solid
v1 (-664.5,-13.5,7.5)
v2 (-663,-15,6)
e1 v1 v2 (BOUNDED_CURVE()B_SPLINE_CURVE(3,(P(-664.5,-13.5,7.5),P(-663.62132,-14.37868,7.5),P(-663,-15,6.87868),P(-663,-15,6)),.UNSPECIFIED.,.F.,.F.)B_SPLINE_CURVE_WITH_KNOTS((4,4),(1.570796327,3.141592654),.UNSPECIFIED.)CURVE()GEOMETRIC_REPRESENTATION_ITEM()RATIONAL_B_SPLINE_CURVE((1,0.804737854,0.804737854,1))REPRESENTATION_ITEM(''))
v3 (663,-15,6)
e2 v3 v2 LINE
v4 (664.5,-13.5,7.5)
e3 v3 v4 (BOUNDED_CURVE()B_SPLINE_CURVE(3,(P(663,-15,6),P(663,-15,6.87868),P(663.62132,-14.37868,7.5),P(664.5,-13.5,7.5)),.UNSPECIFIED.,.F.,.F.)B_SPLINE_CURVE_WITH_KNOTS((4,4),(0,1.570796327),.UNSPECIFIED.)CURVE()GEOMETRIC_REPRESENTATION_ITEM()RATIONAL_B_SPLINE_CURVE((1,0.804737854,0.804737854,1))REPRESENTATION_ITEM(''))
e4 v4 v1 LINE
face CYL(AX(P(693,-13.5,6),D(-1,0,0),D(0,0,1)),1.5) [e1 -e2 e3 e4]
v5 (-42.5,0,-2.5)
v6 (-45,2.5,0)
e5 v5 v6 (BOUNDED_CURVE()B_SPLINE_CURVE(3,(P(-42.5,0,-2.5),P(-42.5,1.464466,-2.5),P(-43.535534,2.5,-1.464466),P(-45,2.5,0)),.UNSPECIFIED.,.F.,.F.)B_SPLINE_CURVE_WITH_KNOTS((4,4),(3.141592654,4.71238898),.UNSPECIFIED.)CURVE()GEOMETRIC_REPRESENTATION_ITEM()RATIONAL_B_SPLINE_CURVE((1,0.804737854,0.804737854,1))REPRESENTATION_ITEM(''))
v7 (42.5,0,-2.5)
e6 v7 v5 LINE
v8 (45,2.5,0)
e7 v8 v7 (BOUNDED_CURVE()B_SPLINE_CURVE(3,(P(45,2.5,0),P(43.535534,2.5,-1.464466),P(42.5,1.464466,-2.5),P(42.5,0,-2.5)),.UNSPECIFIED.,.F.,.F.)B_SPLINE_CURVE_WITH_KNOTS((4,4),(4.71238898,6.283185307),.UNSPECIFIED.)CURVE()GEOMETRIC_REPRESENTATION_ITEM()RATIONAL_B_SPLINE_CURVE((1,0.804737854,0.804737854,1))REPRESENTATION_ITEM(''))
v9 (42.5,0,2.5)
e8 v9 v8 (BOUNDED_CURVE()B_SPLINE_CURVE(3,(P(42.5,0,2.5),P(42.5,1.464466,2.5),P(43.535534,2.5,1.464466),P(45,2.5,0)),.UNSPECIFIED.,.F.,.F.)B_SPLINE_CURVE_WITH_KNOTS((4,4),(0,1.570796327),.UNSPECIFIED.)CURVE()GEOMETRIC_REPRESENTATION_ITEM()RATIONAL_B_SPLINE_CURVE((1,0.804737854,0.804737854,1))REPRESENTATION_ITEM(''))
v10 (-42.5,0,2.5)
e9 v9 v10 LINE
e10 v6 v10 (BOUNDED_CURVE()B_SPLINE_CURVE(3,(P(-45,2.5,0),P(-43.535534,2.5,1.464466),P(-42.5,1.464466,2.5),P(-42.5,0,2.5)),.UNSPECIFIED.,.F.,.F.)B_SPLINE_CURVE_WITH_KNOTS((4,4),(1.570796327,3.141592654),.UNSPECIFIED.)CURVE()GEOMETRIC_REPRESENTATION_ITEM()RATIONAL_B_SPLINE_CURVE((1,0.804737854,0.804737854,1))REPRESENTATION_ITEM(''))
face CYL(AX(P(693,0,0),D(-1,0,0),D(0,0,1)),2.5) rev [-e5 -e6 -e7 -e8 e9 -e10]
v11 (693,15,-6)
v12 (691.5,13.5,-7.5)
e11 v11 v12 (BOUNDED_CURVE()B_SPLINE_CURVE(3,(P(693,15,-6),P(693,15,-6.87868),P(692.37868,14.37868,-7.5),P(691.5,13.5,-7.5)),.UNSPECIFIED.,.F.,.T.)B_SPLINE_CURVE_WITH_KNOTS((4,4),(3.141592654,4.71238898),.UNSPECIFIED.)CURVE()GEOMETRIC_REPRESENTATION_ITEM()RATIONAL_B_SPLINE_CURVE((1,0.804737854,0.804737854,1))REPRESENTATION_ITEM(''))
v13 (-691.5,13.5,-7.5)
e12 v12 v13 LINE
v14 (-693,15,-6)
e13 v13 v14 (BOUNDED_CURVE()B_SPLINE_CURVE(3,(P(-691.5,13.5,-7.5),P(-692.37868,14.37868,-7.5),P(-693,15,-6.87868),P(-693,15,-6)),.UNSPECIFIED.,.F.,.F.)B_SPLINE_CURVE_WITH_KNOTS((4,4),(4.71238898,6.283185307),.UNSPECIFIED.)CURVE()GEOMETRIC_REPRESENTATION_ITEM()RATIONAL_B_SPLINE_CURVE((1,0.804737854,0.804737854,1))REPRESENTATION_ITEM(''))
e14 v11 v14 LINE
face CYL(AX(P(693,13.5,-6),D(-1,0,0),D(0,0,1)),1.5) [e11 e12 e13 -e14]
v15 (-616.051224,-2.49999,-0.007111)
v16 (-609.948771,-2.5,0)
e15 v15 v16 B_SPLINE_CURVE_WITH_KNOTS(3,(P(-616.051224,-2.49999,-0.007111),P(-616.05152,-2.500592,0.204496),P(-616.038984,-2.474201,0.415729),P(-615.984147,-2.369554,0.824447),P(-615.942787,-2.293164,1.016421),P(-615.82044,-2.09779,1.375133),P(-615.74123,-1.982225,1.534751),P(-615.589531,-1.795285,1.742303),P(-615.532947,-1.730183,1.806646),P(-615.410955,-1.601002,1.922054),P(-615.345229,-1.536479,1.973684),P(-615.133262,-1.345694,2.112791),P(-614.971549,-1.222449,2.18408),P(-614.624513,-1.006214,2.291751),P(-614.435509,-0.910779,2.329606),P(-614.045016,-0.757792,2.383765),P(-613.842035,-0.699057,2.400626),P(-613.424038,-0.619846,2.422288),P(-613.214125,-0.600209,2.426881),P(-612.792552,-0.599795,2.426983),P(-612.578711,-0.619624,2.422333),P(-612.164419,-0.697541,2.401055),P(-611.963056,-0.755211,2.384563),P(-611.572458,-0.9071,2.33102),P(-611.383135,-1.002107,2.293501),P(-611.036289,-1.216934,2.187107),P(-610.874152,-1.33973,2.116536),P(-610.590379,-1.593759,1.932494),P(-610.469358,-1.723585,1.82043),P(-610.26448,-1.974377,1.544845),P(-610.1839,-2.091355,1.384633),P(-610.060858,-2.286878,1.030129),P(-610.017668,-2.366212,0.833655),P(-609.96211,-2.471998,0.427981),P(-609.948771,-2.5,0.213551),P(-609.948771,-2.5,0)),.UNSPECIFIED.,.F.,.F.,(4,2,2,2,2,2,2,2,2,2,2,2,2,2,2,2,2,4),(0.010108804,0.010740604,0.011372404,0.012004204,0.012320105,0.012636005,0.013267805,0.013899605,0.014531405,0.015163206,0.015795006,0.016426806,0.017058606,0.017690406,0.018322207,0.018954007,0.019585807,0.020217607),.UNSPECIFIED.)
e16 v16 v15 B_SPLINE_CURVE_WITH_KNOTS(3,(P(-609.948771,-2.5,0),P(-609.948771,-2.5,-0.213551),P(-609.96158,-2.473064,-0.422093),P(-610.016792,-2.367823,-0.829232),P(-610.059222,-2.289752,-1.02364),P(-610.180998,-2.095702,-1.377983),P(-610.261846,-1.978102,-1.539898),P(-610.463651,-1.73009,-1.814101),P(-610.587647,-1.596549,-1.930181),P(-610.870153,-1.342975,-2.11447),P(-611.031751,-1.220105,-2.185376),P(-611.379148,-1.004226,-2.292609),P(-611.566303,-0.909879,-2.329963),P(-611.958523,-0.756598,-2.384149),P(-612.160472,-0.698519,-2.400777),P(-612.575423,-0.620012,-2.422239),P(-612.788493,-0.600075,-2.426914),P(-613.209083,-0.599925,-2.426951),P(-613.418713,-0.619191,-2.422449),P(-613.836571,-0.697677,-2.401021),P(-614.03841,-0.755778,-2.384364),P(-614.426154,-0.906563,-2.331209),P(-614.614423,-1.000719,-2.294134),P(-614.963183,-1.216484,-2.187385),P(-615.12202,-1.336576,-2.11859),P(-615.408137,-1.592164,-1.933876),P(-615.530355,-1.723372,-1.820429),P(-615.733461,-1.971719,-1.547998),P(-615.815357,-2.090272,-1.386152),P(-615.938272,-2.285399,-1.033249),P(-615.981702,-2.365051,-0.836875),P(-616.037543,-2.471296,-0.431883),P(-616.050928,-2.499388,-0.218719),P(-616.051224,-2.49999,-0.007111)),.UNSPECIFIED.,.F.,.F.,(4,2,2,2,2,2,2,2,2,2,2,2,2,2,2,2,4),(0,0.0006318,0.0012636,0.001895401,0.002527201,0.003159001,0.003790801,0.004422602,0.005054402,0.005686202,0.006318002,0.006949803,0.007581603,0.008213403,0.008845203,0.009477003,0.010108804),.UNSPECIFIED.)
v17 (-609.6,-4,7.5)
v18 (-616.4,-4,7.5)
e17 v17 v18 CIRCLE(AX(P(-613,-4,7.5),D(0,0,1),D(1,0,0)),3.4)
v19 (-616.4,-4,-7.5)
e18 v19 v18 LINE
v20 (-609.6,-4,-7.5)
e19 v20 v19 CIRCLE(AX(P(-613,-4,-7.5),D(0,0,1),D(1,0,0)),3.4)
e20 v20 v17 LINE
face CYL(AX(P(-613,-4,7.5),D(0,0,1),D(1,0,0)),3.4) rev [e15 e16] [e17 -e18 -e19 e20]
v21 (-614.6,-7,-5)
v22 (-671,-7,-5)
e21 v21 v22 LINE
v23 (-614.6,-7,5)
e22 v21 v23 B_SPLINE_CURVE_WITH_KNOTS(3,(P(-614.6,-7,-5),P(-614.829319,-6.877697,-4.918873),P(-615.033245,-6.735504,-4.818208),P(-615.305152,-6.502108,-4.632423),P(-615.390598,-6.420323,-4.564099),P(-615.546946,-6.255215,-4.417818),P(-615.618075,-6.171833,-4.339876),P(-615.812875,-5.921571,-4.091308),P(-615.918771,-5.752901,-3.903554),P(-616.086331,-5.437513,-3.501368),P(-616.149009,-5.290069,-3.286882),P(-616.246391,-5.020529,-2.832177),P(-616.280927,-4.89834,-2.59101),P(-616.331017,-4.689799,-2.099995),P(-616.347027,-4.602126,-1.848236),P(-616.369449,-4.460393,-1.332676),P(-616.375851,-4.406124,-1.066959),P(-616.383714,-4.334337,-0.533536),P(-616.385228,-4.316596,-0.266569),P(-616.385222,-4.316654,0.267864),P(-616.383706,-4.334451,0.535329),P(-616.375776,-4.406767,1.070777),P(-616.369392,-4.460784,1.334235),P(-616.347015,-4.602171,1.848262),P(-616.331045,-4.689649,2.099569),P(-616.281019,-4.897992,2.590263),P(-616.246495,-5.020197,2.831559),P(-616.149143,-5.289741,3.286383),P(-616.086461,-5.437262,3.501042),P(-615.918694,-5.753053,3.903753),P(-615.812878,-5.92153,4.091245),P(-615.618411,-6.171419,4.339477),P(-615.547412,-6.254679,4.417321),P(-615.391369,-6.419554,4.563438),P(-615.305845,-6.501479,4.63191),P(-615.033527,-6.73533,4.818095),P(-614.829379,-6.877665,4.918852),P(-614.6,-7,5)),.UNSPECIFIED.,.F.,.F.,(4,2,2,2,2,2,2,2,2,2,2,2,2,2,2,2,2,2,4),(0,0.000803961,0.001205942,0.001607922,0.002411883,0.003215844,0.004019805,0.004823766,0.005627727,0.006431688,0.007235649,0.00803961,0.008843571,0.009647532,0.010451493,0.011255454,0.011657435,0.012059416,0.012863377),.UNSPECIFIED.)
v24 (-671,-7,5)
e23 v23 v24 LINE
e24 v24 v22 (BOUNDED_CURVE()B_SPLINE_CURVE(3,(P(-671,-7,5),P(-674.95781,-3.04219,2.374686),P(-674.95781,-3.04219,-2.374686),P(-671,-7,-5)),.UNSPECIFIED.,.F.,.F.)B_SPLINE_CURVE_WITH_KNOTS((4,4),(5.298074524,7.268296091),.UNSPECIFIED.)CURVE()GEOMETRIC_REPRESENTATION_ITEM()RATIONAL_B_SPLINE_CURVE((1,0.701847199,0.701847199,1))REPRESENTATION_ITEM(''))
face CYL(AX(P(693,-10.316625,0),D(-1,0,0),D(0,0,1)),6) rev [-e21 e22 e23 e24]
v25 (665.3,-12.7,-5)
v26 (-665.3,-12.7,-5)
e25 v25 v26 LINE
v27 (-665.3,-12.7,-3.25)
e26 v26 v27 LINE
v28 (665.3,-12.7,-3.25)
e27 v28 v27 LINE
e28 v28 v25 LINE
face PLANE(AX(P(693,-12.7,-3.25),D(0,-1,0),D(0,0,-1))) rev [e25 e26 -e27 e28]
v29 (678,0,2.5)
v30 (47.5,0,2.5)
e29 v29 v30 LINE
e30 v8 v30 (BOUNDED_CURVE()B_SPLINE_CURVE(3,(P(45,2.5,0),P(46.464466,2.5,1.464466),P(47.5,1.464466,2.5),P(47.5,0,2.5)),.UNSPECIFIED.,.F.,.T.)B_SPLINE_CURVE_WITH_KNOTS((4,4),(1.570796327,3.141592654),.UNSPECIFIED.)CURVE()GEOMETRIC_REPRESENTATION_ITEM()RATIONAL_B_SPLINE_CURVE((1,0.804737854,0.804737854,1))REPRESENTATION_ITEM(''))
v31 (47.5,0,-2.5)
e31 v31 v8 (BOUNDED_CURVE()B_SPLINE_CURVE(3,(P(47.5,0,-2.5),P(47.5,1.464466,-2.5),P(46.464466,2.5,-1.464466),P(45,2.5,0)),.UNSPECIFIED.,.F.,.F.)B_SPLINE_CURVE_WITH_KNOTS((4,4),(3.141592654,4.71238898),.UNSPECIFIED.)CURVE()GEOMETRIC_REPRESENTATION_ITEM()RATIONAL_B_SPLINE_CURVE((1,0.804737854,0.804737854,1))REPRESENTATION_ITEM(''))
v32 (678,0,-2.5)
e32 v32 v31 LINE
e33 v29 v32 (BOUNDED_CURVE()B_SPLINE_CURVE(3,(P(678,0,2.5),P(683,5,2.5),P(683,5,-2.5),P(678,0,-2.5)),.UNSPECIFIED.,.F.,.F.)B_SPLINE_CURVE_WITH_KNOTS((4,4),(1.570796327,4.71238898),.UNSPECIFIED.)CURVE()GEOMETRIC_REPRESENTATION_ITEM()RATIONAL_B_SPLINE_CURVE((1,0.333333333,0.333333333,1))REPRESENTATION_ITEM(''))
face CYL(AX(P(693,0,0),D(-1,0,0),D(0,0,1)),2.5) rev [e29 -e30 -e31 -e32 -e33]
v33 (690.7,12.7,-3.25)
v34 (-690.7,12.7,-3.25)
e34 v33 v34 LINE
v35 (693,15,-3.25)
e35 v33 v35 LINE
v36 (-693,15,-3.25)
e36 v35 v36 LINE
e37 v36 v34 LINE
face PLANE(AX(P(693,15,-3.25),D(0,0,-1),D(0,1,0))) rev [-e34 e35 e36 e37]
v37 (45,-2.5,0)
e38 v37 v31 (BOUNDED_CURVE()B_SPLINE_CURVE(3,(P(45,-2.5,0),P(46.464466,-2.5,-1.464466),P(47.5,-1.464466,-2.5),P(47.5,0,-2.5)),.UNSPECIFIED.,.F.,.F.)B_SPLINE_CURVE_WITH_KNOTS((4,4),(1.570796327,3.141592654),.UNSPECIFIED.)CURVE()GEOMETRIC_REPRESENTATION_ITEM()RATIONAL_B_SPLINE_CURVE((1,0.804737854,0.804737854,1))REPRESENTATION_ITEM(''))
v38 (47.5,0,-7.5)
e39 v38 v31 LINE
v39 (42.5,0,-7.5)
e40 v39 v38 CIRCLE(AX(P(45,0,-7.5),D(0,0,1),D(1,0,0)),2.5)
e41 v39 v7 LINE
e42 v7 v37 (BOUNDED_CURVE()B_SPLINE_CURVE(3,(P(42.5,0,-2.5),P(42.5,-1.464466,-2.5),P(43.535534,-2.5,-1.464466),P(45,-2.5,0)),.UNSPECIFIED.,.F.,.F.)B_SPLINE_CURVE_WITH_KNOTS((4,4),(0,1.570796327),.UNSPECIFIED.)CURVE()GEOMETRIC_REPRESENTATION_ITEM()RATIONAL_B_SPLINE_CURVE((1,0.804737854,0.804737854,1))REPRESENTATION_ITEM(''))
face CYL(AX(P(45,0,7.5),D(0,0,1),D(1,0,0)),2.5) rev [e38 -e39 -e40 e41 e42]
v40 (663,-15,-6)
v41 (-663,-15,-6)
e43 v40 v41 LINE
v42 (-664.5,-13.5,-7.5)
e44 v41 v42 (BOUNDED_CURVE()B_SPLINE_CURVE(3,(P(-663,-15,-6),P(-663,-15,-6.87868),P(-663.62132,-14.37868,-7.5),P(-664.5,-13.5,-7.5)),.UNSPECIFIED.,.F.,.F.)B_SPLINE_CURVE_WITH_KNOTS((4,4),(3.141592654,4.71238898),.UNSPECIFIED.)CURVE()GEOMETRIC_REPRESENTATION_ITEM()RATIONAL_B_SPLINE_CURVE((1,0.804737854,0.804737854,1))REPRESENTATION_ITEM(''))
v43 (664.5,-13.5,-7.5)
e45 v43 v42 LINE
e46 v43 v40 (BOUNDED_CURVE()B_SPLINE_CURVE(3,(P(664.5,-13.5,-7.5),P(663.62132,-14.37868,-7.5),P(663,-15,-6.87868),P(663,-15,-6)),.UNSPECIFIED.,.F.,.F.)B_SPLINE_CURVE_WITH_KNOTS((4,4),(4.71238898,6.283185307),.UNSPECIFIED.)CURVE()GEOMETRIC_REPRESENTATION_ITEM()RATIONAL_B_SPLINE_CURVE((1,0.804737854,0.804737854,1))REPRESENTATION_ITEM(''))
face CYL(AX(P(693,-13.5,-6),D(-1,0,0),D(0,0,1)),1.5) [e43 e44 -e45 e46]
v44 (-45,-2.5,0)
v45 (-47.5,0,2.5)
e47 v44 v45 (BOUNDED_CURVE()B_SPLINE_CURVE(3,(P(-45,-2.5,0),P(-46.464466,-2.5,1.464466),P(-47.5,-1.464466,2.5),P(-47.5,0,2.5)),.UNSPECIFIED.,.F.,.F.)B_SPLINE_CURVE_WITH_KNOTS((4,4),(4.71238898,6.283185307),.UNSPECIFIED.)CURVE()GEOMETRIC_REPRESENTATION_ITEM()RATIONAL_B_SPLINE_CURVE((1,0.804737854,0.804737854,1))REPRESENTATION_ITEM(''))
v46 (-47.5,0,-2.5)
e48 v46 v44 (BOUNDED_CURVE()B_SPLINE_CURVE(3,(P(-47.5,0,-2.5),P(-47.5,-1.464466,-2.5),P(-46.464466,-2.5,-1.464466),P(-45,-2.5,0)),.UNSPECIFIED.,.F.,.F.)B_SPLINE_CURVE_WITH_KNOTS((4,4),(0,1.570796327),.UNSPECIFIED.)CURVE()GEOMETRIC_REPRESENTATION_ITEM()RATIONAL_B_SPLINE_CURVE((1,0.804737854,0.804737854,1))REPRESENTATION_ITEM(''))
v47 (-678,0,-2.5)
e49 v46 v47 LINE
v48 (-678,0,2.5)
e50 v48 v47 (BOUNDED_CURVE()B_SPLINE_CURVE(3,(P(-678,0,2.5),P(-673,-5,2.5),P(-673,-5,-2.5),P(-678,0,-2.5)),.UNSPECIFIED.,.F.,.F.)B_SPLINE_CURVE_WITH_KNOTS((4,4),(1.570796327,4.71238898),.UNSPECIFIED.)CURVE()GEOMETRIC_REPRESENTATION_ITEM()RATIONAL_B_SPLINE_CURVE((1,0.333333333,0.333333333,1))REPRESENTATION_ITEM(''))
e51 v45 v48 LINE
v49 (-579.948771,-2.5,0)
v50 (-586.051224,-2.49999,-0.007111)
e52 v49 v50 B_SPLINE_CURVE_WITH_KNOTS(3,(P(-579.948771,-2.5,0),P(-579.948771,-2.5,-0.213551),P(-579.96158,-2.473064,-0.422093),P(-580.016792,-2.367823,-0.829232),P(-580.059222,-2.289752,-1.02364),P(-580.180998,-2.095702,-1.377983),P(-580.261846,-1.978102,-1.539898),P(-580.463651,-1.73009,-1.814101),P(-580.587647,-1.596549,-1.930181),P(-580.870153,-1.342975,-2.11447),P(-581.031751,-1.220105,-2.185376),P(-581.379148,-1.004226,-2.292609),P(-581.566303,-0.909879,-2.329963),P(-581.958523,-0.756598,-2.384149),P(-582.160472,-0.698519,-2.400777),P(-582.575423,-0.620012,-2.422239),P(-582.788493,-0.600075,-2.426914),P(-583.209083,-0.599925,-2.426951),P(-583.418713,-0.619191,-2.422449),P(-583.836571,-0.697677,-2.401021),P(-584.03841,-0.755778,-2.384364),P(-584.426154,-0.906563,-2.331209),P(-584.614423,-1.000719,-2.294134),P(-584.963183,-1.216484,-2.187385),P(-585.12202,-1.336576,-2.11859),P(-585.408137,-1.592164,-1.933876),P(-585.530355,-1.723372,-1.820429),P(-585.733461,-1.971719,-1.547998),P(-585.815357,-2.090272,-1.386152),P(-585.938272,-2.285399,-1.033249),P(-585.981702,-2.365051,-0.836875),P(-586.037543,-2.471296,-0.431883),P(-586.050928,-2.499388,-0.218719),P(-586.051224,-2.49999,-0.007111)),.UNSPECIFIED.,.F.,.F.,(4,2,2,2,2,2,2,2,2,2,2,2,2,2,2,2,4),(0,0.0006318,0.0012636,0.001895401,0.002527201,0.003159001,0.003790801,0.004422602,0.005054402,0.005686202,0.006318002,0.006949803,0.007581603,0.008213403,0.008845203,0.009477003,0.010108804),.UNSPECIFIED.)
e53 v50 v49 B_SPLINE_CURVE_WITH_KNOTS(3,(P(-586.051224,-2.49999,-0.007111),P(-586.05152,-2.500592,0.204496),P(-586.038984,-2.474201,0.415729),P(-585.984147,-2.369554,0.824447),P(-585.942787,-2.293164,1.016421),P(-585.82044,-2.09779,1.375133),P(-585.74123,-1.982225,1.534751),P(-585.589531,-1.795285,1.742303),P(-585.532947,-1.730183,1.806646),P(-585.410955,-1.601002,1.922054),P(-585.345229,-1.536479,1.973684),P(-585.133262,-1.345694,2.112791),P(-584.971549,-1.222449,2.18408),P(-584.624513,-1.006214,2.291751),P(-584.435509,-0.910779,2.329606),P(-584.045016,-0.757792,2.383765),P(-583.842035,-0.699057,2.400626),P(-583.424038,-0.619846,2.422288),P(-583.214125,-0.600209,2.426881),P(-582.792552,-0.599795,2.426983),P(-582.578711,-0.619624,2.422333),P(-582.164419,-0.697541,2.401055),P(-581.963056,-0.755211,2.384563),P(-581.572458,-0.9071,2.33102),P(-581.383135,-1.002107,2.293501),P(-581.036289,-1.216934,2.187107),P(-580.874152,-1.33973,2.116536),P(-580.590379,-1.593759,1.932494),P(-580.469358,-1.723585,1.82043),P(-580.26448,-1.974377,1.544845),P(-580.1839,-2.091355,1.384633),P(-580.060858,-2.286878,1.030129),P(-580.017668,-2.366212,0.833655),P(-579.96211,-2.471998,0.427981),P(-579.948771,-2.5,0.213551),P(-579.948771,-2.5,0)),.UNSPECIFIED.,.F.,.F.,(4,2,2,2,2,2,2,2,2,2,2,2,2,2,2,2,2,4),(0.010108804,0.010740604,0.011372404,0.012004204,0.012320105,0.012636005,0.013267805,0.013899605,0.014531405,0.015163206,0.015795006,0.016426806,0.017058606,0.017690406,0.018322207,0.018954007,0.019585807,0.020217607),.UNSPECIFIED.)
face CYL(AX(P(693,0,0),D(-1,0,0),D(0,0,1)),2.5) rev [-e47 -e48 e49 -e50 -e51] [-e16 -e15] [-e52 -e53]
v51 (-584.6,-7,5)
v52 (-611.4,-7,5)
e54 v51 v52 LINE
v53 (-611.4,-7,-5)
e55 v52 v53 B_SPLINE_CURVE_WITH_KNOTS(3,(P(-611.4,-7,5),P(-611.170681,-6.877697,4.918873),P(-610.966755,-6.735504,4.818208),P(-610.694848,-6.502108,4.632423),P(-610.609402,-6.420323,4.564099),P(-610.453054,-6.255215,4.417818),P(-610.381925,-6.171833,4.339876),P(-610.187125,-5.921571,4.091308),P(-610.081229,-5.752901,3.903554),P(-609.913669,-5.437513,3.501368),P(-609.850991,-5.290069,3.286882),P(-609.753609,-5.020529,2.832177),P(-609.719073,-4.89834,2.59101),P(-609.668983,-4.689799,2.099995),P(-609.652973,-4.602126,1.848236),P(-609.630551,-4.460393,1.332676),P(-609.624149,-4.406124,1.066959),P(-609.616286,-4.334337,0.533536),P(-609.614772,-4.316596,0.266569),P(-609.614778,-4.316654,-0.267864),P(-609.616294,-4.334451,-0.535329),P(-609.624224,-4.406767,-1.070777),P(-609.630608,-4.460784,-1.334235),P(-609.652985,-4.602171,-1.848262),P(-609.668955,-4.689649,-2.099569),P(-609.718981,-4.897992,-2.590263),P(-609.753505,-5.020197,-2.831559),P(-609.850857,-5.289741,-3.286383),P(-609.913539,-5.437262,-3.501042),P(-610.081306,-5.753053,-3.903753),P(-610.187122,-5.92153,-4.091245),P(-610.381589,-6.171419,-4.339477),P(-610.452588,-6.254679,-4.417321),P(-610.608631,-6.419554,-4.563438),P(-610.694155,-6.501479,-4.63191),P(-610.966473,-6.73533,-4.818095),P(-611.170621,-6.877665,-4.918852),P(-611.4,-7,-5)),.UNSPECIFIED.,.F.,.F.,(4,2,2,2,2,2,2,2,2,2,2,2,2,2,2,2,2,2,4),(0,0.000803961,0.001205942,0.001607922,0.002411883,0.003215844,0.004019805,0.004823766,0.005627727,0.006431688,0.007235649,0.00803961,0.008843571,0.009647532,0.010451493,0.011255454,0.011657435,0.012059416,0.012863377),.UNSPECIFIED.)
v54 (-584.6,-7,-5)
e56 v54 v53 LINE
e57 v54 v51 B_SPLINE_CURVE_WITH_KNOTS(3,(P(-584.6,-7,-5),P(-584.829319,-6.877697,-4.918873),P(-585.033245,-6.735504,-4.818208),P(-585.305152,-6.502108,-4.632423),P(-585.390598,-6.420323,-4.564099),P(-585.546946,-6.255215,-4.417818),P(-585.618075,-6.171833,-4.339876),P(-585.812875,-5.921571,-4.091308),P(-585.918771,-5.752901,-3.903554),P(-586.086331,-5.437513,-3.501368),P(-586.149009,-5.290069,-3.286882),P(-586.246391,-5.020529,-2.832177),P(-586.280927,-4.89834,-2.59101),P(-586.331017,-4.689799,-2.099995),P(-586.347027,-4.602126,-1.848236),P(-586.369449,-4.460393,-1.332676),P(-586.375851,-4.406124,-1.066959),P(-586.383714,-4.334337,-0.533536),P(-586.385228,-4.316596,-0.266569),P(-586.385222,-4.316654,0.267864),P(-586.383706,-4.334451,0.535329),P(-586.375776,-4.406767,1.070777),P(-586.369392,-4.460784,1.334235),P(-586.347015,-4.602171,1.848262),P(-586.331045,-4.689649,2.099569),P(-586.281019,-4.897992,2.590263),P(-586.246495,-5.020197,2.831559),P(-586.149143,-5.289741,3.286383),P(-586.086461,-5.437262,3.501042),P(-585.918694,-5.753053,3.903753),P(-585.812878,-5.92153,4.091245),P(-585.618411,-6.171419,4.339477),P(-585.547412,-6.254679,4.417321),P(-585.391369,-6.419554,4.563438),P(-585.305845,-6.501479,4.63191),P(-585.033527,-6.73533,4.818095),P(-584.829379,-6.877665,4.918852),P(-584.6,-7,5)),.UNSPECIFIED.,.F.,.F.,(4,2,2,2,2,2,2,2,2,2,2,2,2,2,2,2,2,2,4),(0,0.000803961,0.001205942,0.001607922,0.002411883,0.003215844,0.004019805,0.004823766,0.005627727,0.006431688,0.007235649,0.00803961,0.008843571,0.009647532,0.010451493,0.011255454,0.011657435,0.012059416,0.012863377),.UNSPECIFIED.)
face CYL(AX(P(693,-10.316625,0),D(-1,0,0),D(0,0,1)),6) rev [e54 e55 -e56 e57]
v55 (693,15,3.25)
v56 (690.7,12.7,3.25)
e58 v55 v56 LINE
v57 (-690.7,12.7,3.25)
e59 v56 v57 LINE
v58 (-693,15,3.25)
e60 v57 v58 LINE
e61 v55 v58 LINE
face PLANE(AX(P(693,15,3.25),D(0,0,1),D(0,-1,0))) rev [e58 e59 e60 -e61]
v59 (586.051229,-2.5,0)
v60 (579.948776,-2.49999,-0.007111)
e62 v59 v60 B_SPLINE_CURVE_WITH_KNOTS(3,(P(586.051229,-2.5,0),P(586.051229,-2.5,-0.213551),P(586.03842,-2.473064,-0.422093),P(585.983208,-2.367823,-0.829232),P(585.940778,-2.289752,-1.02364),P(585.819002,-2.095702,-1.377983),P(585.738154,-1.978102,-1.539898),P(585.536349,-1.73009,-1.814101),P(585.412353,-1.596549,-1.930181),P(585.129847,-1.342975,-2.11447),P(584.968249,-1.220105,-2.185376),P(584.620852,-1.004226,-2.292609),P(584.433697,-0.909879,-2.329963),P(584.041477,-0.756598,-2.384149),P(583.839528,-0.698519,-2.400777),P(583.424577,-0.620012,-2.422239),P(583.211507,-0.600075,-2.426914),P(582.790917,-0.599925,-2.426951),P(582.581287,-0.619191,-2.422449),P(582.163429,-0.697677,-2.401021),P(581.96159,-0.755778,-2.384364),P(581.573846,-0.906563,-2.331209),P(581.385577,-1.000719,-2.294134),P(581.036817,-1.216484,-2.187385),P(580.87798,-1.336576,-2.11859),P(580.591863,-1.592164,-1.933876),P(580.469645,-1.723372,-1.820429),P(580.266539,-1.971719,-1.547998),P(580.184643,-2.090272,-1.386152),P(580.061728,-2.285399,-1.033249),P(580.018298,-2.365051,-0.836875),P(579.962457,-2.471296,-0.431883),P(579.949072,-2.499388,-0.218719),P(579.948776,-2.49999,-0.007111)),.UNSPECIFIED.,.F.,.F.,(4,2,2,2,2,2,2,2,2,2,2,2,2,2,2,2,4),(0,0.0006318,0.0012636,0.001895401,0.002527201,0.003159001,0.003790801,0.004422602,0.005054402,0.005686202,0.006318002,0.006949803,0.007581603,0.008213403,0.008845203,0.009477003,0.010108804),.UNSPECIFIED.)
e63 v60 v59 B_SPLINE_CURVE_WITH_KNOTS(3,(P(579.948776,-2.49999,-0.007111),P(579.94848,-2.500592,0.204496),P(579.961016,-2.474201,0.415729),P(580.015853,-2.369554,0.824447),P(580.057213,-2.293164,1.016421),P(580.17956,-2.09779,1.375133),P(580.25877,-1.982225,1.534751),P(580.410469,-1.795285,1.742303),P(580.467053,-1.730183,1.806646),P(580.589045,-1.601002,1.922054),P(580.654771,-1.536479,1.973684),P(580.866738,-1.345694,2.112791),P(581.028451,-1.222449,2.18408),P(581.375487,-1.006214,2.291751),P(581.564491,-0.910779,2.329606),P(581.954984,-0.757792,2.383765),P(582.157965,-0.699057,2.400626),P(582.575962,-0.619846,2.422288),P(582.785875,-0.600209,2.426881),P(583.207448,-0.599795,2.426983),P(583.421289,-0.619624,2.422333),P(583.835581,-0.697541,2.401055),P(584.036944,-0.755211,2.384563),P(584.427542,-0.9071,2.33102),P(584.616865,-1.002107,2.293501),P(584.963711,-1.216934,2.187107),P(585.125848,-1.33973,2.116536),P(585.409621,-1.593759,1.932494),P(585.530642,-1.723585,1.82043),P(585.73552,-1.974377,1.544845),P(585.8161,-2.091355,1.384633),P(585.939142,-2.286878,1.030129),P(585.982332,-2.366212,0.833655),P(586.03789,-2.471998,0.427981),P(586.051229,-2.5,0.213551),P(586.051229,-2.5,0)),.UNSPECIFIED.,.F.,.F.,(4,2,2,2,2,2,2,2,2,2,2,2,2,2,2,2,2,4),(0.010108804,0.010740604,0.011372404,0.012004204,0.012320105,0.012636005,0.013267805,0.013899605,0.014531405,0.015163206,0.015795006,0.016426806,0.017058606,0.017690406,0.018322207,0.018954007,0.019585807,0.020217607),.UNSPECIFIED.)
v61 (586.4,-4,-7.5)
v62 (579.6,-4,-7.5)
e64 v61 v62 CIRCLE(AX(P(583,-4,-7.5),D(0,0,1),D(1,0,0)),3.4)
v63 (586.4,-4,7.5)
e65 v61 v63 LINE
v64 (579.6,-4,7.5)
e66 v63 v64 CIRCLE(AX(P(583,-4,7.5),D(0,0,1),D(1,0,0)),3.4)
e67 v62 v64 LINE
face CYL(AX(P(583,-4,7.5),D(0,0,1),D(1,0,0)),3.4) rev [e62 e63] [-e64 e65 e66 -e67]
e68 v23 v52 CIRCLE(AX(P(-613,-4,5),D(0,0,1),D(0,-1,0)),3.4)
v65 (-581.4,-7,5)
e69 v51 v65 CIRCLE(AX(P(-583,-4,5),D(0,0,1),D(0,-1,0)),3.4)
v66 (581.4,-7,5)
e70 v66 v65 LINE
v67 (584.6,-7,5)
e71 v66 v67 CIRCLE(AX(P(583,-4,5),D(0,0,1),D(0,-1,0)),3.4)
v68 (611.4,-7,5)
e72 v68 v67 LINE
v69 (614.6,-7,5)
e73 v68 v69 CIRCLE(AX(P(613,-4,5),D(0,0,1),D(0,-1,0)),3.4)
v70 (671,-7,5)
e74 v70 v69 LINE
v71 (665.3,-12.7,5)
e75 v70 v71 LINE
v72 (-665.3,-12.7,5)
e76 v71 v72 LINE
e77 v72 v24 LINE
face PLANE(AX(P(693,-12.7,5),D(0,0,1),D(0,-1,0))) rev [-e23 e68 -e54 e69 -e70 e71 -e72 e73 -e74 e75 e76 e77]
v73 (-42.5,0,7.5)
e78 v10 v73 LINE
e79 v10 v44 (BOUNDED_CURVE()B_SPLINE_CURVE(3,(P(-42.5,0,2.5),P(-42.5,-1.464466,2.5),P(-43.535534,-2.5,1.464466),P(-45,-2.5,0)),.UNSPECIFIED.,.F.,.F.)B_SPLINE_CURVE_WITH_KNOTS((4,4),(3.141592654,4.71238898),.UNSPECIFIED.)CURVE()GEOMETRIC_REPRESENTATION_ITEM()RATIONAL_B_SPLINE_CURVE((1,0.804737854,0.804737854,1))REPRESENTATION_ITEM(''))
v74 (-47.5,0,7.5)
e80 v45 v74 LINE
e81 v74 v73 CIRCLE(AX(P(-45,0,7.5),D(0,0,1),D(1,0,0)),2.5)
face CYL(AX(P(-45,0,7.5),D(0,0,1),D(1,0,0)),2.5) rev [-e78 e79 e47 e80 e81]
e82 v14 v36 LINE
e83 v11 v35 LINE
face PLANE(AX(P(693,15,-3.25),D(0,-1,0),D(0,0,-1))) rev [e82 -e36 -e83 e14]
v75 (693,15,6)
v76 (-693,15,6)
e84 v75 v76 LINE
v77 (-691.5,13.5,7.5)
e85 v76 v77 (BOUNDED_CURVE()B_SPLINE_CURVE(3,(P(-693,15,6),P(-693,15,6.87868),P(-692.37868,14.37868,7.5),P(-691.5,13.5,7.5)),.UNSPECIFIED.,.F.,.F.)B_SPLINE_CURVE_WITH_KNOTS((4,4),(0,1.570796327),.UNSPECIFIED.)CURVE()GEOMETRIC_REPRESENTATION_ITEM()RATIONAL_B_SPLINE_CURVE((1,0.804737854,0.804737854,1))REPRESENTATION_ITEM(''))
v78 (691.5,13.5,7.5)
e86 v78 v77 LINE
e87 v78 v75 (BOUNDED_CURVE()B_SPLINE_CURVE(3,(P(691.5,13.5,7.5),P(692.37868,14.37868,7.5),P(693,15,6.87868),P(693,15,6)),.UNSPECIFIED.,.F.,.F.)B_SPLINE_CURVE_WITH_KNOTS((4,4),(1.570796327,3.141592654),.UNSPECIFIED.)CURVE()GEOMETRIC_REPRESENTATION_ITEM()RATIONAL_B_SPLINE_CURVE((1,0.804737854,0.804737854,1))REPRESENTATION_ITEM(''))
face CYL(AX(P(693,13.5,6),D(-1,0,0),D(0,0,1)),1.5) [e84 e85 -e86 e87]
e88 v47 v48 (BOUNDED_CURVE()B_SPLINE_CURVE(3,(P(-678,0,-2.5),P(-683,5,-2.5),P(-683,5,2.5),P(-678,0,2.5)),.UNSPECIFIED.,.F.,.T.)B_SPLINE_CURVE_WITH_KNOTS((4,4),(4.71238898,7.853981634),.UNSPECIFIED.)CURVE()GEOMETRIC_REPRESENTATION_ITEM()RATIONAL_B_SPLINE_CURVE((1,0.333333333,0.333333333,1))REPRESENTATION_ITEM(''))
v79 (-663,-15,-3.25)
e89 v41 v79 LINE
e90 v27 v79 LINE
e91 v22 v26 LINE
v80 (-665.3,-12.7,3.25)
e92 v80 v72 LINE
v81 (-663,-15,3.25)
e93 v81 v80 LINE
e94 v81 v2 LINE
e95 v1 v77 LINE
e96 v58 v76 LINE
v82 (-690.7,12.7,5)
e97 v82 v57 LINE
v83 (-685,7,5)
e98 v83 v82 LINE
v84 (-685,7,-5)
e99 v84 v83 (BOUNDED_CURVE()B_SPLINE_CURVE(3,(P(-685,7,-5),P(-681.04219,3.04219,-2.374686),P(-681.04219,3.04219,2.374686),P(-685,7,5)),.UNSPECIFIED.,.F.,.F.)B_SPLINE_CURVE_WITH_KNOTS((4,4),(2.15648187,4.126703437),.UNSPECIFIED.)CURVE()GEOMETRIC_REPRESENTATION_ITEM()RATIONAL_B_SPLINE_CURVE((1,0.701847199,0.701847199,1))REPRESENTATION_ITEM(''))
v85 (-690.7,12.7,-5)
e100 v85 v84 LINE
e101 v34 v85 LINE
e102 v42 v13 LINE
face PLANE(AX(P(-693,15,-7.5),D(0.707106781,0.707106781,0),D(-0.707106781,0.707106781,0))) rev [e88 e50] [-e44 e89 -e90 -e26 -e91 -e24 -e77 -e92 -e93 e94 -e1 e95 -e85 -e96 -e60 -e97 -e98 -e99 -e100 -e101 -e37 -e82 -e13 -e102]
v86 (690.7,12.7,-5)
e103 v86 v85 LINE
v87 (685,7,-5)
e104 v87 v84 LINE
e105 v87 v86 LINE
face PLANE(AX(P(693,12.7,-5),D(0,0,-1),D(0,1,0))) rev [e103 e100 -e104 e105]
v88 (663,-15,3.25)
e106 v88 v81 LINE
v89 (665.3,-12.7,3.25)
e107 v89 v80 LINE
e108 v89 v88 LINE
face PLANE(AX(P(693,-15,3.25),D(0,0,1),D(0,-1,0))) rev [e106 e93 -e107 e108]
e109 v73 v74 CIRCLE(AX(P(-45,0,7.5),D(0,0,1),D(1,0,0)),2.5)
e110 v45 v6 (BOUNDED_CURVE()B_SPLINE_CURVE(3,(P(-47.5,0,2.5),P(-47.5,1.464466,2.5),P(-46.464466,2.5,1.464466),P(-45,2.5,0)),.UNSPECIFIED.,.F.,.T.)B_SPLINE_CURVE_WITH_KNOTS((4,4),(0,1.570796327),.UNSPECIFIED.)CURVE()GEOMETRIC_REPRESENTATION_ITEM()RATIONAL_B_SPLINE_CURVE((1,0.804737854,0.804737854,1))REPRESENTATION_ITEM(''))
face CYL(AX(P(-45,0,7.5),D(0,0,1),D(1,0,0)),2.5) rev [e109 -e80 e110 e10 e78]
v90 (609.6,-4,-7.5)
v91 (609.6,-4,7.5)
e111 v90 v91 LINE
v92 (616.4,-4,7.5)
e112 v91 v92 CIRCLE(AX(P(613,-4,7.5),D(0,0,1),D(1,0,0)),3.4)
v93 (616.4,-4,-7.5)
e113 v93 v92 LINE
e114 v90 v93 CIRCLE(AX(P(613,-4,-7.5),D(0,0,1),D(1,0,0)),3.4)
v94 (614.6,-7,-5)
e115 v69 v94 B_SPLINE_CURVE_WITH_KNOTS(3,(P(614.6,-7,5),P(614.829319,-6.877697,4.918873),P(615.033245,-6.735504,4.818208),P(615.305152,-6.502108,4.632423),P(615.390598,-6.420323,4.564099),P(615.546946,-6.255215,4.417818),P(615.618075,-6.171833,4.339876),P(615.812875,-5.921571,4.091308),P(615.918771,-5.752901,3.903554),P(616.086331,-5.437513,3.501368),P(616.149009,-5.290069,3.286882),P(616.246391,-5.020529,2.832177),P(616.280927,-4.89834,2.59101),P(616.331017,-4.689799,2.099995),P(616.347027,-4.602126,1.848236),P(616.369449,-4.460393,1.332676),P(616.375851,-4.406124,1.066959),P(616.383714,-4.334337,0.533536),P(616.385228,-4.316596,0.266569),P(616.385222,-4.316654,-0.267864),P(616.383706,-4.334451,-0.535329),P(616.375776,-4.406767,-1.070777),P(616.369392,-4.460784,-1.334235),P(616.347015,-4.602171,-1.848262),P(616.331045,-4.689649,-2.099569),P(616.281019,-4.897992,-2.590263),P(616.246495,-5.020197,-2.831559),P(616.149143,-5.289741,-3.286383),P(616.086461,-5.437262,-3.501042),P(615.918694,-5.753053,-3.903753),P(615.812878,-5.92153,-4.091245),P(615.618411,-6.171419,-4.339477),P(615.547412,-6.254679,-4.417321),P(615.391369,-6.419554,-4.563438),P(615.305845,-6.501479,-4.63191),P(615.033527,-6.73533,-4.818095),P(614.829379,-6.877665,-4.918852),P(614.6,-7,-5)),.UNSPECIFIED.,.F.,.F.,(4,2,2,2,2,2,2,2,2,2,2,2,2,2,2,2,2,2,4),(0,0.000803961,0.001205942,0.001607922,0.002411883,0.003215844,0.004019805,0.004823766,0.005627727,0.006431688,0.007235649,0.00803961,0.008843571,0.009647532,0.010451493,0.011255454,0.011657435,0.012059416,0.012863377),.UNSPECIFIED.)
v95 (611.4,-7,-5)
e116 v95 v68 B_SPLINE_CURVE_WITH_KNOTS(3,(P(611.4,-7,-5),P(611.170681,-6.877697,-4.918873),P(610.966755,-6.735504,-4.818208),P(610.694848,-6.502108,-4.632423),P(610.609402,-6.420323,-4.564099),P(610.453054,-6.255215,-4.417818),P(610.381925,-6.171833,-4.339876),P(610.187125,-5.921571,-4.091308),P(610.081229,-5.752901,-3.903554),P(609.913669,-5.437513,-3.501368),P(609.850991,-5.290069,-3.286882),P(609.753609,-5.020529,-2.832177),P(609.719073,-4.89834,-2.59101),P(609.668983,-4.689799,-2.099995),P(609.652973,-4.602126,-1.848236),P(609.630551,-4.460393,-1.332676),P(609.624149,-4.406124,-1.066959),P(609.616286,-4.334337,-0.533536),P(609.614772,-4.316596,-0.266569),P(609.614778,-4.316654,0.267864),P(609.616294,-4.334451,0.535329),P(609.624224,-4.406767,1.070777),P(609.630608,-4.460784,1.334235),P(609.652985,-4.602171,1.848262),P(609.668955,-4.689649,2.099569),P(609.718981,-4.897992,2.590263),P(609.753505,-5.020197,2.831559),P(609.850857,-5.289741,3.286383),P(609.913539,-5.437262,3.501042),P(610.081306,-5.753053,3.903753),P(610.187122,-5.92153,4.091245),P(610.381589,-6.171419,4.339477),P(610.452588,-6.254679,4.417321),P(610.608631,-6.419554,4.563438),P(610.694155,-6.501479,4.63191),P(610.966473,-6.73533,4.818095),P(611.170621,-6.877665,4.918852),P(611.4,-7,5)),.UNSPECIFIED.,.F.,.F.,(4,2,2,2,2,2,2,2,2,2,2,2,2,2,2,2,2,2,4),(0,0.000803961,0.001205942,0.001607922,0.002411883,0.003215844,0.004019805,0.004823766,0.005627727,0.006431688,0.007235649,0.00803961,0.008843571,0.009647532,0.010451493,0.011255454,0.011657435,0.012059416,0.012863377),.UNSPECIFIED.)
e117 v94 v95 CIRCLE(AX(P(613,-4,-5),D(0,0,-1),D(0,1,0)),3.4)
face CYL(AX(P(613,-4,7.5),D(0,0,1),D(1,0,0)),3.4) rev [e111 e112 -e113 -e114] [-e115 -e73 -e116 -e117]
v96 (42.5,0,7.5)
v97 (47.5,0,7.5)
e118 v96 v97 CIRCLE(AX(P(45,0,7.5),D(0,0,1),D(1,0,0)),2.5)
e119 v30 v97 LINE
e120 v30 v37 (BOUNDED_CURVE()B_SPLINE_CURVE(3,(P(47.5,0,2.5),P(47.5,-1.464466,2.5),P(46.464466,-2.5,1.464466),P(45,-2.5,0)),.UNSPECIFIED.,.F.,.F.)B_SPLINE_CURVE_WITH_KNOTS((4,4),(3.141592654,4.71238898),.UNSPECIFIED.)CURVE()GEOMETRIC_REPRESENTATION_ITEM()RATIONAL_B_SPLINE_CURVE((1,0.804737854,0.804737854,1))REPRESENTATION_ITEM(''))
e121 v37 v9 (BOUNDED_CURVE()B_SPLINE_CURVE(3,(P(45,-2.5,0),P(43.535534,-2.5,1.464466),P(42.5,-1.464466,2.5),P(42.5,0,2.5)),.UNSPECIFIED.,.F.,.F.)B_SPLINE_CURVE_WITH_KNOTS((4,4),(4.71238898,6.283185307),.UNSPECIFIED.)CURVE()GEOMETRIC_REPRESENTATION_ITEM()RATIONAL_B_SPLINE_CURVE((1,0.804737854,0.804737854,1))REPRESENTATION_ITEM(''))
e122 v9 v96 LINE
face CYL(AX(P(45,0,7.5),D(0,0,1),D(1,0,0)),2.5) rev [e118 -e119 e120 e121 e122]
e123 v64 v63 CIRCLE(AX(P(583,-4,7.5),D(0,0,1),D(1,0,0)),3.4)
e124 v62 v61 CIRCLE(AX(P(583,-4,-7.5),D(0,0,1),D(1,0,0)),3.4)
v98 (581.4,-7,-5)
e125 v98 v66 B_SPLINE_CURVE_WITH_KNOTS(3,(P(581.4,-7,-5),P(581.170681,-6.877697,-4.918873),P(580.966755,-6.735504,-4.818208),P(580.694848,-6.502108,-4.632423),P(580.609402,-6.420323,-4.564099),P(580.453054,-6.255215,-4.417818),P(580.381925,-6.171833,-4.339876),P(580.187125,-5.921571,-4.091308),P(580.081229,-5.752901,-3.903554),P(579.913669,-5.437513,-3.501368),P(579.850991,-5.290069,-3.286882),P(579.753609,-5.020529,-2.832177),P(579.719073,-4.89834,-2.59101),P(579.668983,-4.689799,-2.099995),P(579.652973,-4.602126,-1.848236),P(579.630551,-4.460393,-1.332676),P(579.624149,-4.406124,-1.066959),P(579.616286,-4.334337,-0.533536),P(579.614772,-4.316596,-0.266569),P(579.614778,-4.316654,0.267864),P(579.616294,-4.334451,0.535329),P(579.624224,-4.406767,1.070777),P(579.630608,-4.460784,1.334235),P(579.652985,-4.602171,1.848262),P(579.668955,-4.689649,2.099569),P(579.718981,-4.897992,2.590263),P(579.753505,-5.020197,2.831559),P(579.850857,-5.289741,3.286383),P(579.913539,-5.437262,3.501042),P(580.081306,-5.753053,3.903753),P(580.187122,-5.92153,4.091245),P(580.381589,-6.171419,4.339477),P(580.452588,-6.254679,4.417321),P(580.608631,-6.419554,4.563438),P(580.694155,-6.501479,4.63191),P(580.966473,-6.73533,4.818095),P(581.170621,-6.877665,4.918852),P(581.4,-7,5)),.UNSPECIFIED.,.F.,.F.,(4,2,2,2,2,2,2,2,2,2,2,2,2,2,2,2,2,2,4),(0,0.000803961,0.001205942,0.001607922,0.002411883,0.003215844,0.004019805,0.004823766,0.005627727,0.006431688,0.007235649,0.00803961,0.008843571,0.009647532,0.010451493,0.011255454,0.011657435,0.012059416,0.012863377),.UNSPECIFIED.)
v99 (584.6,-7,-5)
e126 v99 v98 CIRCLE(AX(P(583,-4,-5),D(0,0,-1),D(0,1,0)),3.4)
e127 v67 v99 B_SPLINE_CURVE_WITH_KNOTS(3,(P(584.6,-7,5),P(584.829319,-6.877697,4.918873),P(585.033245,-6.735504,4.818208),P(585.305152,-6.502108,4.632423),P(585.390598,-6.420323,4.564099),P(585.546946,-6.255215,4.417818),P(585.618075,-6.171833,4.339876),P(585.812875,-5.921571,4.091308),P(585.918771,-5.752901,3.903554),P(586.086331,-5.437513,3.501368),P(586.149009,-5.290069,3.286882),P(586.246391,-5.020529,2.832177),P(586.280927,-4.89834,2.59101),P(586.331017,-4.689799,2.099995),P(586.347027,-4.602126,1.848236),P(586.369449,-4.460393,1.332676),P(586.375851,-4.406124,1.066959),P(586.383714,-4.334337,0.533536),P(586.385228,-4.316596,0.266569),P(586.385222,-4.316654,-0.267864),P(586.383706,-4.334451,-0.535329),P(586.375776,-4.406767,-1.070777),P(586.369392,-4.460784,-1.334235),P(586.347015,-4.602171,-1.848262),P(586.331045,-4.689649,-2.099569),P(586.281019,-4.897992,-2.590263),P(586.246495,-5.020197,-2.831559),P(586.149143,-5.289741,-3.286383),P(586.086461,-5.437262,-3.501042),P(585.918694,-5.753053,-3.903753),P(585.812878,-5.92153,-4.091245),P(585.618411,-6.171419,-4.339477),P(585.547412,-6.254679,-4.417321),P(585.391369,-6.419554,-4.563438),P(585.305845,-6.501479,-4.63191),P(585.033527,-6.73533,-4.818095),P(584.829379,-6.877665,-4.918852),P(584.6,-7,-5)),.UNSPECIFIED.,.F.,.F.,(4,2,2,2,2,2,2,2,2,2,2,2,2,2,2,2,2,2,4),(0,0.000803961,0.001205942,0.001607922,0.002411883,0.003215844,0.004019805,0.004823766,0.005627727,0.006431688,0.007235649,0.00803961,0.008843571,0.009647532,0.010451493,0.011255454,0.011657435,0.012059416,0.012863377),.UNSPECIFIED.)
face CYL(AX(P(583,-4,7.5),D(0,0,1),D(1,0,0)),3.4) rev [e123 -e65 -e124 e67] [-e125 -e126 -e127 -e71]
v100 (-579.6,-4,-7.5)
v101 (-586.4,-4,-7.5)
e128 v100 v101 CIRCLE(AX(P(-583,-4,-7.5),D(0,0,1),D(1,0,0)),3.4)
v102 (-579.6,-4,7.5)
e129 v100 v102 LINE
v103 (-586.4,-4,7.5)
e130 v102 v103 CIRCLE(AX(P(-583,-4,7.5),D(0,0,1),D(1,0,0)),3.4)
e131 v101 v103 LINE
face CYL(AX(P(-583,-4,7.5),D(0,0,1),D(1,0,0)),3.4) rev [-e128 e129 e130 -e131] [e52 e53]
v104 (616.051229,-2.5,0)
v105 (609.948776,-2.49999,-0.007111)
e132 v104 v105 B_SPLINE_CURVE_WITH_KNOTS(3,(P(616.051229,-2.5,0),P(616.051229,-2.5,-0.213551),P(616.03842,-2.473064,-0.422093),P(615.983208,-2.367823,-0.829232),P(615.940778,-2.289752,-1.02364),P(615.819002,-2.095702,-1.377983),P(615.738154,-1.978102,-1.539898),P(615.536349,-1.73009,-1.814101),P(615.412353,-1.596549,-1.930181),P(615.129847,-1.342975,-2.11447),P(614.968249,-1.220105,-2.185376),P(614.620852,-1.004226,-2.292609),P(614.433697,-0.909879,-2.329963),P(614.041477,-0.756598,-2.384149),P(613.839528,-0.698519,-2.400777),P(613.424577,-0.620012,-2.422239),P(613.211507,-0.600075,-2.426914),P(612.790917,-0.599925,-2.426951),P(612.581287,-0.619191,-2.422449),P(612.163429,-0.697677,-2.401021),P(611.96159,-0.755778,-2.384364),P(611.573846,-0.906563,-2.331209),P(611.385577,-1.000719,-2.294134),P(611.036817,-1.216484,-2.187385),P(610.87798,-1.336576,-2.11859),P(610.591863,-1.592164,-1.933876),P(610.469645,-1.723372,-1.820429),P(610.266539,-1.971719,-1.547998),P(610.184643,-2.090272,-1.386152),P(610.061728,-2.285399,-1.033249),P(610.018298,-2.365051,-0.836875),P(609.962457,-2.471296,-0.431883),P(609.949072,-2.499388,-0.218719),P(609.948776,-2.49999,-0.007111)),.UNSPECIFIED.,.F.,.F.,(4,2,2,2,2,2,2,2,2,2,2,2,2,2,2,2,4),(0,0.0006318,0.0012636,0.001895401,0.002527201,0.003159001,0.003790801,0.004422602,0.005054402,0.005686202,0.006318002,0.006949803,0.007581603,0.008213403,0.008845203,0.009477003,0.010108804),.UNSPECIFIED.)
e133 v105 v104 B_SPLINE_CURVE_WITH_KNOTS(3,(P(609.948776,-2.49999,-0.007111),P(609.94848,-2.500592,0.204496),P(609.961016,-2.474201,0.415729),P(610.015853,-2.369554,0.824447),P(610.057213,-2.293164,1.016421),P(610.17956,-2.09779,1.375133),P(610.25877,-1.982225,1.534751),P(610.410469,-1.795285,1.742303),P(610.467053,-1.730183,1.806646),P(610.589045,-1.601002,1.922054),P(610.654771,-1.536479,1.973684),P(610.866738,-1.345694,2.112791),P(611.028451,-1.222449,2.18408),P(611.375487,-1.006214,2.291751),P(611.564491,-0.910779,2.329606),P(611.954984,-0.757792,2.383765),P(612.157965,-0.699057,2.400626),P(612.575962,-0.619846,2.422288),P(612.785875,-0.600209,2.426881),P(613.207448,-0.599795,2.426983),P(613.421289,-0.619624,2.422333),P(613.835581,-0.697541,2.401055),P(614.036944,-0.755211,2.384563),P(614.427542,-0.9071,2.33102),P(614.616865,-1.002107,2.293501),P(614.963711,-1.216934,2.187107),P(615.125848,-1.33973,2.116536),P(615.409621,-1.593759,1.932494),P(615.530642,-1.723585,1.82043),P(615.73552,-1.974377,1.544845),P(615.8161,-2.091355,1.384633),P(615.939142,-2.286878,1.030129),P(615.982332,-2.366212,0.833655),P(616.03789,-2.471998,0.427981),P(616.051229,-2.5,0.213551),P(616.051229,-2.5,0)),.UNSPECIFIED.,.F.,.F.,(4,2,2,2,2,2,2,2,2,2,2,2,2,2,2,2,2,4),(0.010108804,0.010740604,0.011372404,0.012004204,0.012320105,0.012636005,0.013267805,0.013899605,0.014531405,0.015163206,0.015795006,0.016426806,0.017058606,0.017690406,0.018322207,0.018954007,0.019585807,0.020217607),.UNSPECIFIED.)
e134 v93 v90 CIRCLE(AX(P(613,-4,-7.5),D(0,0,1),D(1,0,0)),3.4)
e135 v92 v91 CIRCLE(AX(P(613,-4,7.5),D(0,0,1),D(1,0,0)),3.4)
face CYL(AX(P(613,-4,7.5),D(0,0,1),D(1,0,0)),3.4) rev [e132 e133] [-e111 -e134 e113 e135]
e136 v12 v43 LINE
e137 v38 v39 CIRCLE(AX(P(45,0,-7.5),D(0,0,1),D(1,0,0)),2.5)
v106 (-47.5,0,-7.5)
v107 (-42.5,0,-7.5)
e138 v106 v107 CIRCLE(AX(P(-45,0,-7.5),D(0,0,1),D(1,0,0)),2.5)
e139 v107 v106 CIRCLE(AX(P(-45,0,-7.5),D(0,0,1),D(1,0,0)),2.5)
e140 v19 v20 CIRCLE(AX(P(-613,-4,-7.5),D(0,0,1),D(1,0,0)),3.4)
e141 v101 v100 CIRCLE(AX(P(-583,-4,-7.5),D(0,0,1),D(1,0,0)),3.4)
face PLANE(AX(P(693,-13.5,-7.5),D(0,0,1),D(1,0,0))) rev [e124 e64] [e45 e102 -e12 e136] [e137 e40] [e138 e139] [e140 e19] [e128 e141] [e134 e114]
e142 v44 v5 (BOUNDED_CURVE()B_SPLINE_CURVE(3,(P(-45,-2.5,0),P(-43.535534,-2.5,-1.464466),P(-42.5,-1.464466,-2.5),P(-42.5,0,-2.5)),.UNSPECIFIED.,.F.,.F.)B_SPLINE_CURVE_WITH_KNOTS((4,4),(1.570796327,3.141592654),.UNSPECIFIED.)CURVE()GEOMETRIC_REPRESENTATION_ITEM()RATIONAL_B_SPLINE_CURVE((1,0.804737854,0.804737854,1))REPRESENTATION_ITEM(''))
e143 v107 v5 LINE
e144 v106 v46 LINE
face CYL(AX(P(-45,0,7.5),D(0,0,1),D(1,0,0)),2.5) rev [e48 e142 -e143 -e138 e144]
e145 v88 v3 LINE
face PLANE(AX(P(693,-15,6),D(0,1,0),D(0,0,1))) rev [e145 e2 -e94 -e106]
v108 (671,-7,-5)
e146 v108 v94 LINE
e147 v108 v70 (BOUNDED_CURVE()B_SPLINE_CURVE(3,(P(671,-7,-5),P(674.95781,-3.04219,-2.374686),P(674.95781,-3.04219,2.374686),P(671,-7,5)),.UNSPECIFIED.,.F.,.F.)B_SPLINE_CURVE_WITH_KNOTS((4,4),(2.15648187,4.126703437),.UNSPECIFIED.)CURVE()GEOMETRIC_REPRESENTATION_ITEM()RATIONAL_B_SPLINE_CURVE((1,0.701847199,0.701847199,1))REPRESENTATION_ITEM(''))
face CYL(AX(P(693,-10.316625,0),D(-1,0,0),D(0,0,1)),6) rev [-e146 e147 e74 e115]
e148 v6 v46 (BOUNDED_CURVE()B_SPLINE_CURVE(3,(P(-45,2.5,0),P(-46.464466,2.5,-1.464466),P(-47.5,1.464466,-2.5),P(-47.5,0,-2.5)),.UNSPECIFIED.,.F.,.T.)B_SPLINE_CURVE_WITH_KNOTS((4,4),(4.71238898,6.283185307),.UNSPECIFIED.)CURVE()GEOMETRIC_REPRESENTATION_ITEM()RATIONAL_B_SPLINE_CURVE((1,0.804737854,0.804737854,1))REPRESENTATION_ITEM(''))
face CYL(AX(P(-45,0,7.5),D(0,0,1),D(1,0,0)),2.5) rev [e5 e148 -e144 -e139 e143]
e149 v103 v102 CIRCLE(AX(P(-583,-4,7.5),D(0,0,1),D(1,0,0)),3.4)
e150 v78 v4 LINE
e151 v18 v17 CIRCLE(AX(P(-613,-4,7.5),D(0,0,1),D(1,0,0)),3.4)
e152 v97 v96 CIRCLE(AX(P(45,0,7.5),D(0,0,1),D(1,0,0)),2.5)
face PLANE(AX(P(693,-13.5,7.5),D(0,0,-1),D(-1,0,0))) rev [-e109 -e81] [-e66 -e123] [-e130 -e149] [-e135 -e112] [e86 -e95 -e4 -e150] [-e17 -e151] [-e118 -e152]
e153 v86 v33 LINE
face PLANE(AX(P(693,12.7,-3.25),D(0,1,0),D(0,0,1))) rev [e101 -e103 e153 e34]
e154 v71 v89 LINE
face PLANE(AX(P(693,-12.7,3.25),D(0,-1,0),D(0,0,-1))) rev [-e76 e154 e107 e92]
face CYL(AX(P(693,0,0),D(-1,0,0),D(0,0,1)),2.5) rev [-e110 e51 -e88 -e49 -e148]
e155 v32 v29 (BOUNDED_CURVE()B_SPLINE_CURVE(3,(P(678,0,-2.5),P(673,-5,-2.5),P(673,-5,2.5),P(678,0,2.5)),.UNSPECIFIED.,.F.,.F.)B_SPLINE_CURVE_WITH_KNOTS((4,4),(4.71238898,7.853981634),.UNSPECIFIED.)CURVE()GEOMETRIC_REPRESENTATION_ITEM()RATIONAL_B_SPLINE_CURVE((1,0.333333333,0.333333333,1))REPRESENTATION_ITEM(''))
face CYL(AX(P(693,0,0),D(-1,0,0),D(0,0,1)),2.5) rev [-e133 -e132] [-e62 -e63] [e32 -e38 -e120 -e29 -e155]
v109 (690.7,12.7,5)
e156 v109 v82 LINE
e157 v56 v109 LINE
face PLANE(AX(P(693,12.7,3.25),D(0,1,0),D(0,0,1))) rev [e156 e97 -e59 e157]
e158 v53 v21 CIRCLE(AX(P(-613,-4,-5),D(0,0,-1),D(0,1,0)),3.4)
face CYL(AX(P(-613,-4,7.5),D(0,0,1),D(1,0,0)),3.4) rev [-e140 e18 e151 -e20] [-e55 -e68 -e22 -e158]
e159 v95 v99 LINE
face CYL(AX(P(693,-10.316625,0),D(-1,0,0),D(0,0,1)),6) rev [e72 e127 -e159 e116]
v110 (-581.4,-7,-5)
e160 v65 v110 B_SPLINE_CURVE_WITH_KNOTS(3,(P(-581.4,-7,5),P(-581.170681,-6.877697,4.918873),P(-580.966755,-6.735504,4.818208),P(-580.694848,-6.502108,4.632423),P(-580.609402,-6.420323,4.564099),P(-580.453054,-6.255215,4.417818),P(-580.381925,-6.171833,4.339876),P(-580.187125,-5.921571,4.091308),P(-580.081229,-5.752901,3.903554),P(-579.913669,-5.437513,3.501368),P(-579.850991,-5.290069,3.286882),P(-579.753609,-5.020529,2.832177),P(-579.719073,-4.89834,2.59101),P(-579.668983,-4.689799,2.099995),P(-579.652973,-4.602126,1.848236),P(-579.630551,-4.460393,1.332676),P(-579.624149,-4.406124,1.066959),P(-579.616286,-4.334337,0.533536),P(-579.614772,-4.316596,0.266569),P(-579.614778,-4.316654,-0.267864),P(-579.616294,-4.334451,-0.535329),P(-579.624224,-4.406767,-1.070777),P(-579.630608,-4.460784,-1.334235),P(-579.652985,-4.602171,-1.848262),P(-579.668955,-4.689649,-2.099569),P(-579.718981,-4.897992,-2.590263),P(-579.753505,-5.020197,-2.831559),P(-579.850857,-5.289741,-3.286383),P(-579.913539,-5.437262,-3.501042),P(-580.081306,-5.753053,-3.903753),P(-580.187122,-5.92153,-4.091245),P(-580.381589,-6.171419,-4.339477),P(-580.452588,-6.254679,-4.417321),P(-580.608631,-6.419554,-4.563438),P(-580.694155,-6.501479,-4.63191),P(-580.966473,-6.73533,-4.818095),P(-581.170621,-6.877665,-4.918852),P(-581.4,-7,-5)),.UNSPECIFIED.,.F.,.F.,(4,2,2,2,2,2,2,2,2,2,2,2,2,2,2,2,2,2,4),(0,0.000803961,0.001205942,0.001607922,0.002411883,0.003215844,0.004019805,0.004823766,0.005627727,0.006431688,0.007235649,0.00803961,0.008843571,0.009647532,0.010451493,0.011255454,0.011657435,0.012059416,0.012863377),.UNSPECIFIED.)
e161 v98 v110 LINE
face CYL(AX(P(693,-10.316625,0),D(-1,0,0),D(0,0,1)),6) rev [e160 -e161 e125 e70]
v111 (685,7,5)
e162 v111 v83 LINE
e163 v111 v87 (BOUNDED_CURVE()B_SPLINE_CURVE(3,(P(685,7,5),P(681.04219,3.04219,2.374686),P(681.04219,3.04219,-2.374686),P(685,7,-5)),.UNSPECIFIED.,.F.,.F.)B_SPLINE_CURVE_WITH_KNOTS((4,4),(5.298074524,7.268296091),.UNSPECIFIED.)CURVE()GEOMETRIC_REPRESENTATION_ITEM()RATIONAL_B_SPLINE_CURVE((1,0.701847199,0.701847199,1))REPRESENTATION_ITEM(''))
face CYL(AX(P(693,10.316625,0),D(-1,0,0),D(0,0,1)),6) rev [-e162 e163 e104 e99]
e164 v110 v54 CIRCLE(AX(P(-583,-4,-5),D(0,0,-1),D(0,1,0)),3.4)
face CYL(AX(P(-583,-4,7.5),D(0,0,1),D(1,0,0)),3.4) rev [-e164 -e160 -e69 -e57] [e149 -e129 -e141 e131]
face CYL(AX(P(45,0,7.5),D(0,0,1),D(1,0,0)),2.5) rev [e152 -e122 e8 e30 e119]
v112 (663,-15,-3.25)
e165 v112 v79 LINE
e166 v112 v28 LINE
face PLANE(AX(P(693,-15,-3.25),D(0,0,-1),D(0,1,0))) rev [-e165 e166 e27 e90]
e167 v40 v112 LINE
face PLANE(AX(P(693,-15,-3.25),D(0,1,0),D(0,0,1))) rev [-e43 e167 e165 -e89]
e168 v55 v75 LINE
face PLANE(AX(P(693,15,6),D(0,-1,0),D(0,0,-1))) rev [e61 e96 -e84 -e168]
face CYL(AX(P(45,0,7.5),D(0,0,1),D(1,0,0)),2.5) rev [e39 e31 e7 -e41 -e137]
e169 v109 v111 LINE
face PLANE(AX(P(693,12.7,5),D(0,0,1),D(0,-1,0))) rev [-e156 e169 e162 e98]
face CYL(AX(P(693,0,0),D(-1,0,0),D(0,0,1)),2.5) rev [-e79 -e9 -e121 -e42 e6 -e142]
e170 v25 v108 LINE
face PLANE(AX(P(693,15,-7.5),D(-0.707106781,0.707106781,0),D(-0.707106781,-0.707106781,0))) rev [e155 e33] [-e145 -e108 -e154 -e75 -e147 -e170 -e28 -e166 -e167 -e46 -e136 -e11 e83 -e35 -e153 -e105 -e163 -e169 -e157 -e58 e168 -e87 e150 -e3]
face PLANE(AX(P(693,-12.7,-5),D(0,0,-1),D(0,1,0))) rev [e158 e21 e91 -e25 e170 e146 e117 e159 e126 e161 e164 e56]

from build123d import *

# Parameters (mm, degrees)
SKETCH11_R             = 2.5
MEMBER_1_DEPTH         = 1386
CUT_EXTRUDE_1_DEPTH    = 694.324599304
HOLE_WIZARD_M8_1_D     = 6.8
HOLE_WIZARD_M6_1_D     = 5
HOLE_WIZARD_M6_1_DEPTH = 17
HOLE_WIZARD_M6_1_TIP   = 1.502151548


with BuildPart() as part:
    # Sketch11 → Member 1 (new body)
    with BuildSketch(Plane(origin=(-693, 0, 0), x_dir=(0, 0, -1), z_dir=(1, 0, 0))):
        with BuildLine():
            Line((-6, -15), (-3.25, -15))
            Line((-3.25, -15), (-3.25, -12.7))
            Line((-3.25, -12.7), (-5, -12.7))
            Line((-5, -12.7), (-5, -7))
            ThreePointArc((-5, -7), (0, -4.31662479), (5, -7))
            Line((5, -7), (5, -12.7))
            Line((5, -12.7), (3.25, -12.7))
            Line((3.25, -12.7), (3.25, -15))
            Line((3.25, -15), (6, -15))
            ThreePointArc((6, -15), (7.060660172, -14.560660172), (7.5, -13.5))
            Line((7.5, -13.5), (7.5, 13.5))
            ThreePointArc((7.5, 13.5), (7.060660172, 14.560660172), (6, 15))
            Line((6, 15), (3.25, 15))
            Line((3.25, 15), (3.25, 12.7))
            Line((3.25, 12.7), (5, 12.7))
            Line((5, 12.7), (5, 7))
            ThreePointArc((5, 7), (0, 4.31662479), (-5, 7))
            Line((-5, 7), (-5, 12.7))
            Line((-5, 12.7), (-3.25, 12.7))
            Line((-3.25, 12.7), (-3.25, 15))
            Line((-3.25, 15), (-6, 15))
            ThreePointArc((-6, 15), (-7.060660172, 14.560660172), (-7.5, 13.5))
            Line((-7.5, 13.5), (-7.5, -13.5))
            ThreePointArc((-7.5, -13.5), (-7.060660172, -14.560660172), (-6, -15))
        make_face()
        Circle(SKETCH11_R, mode=Mode.SUBTRACT)
    extrude(amount=MEMBER_1_DEPTH)

    # 草图4 → 切除-拉伸1 (cut, through all)
    with BuildSketch(Plane.XY.offset(7.5)):
        Polygon((-693, 15), (-663, -15), (-693, -15), align=None)
        Polygon((693, -15), (693, 15), (663, -15), align=None)
    extrude(amount=-CUT_EXTRUDE_1_DEPTH, mode=Mode.SUBTRACT)

    # M8 螺纹孔1 (through all)
    with Locations(Plane.XY.offset(7.5)):
        with Locations((-613, -4), (-583, -4), (583, -4), (613, -4)):
            Hole(HOLE_WIZARD_M8_1_D / 2)

    # M6 螺纹孔1
    with Locations(Plane.XY.offset(7.5)):
        with Locations((-45, 0), (45, 0)):
            Hole(HOLE_WIZARD_M6_1_D / 2, depth=HOLE_WIZARD_M6_1_DEPTH)
            with Locations((0, 0, -(HOLE_WIZARD_M6_1_DEPTH + HOLE_WIZARD_M6_1_TIP / 2))):  # 118° drill point
                Cone(0, HOLE_WIZARD_M6_1_D / 2, HOLE_WIZARD_M6_1_TIP, mode=Mode.SUBTRACT)


solid = part.part
